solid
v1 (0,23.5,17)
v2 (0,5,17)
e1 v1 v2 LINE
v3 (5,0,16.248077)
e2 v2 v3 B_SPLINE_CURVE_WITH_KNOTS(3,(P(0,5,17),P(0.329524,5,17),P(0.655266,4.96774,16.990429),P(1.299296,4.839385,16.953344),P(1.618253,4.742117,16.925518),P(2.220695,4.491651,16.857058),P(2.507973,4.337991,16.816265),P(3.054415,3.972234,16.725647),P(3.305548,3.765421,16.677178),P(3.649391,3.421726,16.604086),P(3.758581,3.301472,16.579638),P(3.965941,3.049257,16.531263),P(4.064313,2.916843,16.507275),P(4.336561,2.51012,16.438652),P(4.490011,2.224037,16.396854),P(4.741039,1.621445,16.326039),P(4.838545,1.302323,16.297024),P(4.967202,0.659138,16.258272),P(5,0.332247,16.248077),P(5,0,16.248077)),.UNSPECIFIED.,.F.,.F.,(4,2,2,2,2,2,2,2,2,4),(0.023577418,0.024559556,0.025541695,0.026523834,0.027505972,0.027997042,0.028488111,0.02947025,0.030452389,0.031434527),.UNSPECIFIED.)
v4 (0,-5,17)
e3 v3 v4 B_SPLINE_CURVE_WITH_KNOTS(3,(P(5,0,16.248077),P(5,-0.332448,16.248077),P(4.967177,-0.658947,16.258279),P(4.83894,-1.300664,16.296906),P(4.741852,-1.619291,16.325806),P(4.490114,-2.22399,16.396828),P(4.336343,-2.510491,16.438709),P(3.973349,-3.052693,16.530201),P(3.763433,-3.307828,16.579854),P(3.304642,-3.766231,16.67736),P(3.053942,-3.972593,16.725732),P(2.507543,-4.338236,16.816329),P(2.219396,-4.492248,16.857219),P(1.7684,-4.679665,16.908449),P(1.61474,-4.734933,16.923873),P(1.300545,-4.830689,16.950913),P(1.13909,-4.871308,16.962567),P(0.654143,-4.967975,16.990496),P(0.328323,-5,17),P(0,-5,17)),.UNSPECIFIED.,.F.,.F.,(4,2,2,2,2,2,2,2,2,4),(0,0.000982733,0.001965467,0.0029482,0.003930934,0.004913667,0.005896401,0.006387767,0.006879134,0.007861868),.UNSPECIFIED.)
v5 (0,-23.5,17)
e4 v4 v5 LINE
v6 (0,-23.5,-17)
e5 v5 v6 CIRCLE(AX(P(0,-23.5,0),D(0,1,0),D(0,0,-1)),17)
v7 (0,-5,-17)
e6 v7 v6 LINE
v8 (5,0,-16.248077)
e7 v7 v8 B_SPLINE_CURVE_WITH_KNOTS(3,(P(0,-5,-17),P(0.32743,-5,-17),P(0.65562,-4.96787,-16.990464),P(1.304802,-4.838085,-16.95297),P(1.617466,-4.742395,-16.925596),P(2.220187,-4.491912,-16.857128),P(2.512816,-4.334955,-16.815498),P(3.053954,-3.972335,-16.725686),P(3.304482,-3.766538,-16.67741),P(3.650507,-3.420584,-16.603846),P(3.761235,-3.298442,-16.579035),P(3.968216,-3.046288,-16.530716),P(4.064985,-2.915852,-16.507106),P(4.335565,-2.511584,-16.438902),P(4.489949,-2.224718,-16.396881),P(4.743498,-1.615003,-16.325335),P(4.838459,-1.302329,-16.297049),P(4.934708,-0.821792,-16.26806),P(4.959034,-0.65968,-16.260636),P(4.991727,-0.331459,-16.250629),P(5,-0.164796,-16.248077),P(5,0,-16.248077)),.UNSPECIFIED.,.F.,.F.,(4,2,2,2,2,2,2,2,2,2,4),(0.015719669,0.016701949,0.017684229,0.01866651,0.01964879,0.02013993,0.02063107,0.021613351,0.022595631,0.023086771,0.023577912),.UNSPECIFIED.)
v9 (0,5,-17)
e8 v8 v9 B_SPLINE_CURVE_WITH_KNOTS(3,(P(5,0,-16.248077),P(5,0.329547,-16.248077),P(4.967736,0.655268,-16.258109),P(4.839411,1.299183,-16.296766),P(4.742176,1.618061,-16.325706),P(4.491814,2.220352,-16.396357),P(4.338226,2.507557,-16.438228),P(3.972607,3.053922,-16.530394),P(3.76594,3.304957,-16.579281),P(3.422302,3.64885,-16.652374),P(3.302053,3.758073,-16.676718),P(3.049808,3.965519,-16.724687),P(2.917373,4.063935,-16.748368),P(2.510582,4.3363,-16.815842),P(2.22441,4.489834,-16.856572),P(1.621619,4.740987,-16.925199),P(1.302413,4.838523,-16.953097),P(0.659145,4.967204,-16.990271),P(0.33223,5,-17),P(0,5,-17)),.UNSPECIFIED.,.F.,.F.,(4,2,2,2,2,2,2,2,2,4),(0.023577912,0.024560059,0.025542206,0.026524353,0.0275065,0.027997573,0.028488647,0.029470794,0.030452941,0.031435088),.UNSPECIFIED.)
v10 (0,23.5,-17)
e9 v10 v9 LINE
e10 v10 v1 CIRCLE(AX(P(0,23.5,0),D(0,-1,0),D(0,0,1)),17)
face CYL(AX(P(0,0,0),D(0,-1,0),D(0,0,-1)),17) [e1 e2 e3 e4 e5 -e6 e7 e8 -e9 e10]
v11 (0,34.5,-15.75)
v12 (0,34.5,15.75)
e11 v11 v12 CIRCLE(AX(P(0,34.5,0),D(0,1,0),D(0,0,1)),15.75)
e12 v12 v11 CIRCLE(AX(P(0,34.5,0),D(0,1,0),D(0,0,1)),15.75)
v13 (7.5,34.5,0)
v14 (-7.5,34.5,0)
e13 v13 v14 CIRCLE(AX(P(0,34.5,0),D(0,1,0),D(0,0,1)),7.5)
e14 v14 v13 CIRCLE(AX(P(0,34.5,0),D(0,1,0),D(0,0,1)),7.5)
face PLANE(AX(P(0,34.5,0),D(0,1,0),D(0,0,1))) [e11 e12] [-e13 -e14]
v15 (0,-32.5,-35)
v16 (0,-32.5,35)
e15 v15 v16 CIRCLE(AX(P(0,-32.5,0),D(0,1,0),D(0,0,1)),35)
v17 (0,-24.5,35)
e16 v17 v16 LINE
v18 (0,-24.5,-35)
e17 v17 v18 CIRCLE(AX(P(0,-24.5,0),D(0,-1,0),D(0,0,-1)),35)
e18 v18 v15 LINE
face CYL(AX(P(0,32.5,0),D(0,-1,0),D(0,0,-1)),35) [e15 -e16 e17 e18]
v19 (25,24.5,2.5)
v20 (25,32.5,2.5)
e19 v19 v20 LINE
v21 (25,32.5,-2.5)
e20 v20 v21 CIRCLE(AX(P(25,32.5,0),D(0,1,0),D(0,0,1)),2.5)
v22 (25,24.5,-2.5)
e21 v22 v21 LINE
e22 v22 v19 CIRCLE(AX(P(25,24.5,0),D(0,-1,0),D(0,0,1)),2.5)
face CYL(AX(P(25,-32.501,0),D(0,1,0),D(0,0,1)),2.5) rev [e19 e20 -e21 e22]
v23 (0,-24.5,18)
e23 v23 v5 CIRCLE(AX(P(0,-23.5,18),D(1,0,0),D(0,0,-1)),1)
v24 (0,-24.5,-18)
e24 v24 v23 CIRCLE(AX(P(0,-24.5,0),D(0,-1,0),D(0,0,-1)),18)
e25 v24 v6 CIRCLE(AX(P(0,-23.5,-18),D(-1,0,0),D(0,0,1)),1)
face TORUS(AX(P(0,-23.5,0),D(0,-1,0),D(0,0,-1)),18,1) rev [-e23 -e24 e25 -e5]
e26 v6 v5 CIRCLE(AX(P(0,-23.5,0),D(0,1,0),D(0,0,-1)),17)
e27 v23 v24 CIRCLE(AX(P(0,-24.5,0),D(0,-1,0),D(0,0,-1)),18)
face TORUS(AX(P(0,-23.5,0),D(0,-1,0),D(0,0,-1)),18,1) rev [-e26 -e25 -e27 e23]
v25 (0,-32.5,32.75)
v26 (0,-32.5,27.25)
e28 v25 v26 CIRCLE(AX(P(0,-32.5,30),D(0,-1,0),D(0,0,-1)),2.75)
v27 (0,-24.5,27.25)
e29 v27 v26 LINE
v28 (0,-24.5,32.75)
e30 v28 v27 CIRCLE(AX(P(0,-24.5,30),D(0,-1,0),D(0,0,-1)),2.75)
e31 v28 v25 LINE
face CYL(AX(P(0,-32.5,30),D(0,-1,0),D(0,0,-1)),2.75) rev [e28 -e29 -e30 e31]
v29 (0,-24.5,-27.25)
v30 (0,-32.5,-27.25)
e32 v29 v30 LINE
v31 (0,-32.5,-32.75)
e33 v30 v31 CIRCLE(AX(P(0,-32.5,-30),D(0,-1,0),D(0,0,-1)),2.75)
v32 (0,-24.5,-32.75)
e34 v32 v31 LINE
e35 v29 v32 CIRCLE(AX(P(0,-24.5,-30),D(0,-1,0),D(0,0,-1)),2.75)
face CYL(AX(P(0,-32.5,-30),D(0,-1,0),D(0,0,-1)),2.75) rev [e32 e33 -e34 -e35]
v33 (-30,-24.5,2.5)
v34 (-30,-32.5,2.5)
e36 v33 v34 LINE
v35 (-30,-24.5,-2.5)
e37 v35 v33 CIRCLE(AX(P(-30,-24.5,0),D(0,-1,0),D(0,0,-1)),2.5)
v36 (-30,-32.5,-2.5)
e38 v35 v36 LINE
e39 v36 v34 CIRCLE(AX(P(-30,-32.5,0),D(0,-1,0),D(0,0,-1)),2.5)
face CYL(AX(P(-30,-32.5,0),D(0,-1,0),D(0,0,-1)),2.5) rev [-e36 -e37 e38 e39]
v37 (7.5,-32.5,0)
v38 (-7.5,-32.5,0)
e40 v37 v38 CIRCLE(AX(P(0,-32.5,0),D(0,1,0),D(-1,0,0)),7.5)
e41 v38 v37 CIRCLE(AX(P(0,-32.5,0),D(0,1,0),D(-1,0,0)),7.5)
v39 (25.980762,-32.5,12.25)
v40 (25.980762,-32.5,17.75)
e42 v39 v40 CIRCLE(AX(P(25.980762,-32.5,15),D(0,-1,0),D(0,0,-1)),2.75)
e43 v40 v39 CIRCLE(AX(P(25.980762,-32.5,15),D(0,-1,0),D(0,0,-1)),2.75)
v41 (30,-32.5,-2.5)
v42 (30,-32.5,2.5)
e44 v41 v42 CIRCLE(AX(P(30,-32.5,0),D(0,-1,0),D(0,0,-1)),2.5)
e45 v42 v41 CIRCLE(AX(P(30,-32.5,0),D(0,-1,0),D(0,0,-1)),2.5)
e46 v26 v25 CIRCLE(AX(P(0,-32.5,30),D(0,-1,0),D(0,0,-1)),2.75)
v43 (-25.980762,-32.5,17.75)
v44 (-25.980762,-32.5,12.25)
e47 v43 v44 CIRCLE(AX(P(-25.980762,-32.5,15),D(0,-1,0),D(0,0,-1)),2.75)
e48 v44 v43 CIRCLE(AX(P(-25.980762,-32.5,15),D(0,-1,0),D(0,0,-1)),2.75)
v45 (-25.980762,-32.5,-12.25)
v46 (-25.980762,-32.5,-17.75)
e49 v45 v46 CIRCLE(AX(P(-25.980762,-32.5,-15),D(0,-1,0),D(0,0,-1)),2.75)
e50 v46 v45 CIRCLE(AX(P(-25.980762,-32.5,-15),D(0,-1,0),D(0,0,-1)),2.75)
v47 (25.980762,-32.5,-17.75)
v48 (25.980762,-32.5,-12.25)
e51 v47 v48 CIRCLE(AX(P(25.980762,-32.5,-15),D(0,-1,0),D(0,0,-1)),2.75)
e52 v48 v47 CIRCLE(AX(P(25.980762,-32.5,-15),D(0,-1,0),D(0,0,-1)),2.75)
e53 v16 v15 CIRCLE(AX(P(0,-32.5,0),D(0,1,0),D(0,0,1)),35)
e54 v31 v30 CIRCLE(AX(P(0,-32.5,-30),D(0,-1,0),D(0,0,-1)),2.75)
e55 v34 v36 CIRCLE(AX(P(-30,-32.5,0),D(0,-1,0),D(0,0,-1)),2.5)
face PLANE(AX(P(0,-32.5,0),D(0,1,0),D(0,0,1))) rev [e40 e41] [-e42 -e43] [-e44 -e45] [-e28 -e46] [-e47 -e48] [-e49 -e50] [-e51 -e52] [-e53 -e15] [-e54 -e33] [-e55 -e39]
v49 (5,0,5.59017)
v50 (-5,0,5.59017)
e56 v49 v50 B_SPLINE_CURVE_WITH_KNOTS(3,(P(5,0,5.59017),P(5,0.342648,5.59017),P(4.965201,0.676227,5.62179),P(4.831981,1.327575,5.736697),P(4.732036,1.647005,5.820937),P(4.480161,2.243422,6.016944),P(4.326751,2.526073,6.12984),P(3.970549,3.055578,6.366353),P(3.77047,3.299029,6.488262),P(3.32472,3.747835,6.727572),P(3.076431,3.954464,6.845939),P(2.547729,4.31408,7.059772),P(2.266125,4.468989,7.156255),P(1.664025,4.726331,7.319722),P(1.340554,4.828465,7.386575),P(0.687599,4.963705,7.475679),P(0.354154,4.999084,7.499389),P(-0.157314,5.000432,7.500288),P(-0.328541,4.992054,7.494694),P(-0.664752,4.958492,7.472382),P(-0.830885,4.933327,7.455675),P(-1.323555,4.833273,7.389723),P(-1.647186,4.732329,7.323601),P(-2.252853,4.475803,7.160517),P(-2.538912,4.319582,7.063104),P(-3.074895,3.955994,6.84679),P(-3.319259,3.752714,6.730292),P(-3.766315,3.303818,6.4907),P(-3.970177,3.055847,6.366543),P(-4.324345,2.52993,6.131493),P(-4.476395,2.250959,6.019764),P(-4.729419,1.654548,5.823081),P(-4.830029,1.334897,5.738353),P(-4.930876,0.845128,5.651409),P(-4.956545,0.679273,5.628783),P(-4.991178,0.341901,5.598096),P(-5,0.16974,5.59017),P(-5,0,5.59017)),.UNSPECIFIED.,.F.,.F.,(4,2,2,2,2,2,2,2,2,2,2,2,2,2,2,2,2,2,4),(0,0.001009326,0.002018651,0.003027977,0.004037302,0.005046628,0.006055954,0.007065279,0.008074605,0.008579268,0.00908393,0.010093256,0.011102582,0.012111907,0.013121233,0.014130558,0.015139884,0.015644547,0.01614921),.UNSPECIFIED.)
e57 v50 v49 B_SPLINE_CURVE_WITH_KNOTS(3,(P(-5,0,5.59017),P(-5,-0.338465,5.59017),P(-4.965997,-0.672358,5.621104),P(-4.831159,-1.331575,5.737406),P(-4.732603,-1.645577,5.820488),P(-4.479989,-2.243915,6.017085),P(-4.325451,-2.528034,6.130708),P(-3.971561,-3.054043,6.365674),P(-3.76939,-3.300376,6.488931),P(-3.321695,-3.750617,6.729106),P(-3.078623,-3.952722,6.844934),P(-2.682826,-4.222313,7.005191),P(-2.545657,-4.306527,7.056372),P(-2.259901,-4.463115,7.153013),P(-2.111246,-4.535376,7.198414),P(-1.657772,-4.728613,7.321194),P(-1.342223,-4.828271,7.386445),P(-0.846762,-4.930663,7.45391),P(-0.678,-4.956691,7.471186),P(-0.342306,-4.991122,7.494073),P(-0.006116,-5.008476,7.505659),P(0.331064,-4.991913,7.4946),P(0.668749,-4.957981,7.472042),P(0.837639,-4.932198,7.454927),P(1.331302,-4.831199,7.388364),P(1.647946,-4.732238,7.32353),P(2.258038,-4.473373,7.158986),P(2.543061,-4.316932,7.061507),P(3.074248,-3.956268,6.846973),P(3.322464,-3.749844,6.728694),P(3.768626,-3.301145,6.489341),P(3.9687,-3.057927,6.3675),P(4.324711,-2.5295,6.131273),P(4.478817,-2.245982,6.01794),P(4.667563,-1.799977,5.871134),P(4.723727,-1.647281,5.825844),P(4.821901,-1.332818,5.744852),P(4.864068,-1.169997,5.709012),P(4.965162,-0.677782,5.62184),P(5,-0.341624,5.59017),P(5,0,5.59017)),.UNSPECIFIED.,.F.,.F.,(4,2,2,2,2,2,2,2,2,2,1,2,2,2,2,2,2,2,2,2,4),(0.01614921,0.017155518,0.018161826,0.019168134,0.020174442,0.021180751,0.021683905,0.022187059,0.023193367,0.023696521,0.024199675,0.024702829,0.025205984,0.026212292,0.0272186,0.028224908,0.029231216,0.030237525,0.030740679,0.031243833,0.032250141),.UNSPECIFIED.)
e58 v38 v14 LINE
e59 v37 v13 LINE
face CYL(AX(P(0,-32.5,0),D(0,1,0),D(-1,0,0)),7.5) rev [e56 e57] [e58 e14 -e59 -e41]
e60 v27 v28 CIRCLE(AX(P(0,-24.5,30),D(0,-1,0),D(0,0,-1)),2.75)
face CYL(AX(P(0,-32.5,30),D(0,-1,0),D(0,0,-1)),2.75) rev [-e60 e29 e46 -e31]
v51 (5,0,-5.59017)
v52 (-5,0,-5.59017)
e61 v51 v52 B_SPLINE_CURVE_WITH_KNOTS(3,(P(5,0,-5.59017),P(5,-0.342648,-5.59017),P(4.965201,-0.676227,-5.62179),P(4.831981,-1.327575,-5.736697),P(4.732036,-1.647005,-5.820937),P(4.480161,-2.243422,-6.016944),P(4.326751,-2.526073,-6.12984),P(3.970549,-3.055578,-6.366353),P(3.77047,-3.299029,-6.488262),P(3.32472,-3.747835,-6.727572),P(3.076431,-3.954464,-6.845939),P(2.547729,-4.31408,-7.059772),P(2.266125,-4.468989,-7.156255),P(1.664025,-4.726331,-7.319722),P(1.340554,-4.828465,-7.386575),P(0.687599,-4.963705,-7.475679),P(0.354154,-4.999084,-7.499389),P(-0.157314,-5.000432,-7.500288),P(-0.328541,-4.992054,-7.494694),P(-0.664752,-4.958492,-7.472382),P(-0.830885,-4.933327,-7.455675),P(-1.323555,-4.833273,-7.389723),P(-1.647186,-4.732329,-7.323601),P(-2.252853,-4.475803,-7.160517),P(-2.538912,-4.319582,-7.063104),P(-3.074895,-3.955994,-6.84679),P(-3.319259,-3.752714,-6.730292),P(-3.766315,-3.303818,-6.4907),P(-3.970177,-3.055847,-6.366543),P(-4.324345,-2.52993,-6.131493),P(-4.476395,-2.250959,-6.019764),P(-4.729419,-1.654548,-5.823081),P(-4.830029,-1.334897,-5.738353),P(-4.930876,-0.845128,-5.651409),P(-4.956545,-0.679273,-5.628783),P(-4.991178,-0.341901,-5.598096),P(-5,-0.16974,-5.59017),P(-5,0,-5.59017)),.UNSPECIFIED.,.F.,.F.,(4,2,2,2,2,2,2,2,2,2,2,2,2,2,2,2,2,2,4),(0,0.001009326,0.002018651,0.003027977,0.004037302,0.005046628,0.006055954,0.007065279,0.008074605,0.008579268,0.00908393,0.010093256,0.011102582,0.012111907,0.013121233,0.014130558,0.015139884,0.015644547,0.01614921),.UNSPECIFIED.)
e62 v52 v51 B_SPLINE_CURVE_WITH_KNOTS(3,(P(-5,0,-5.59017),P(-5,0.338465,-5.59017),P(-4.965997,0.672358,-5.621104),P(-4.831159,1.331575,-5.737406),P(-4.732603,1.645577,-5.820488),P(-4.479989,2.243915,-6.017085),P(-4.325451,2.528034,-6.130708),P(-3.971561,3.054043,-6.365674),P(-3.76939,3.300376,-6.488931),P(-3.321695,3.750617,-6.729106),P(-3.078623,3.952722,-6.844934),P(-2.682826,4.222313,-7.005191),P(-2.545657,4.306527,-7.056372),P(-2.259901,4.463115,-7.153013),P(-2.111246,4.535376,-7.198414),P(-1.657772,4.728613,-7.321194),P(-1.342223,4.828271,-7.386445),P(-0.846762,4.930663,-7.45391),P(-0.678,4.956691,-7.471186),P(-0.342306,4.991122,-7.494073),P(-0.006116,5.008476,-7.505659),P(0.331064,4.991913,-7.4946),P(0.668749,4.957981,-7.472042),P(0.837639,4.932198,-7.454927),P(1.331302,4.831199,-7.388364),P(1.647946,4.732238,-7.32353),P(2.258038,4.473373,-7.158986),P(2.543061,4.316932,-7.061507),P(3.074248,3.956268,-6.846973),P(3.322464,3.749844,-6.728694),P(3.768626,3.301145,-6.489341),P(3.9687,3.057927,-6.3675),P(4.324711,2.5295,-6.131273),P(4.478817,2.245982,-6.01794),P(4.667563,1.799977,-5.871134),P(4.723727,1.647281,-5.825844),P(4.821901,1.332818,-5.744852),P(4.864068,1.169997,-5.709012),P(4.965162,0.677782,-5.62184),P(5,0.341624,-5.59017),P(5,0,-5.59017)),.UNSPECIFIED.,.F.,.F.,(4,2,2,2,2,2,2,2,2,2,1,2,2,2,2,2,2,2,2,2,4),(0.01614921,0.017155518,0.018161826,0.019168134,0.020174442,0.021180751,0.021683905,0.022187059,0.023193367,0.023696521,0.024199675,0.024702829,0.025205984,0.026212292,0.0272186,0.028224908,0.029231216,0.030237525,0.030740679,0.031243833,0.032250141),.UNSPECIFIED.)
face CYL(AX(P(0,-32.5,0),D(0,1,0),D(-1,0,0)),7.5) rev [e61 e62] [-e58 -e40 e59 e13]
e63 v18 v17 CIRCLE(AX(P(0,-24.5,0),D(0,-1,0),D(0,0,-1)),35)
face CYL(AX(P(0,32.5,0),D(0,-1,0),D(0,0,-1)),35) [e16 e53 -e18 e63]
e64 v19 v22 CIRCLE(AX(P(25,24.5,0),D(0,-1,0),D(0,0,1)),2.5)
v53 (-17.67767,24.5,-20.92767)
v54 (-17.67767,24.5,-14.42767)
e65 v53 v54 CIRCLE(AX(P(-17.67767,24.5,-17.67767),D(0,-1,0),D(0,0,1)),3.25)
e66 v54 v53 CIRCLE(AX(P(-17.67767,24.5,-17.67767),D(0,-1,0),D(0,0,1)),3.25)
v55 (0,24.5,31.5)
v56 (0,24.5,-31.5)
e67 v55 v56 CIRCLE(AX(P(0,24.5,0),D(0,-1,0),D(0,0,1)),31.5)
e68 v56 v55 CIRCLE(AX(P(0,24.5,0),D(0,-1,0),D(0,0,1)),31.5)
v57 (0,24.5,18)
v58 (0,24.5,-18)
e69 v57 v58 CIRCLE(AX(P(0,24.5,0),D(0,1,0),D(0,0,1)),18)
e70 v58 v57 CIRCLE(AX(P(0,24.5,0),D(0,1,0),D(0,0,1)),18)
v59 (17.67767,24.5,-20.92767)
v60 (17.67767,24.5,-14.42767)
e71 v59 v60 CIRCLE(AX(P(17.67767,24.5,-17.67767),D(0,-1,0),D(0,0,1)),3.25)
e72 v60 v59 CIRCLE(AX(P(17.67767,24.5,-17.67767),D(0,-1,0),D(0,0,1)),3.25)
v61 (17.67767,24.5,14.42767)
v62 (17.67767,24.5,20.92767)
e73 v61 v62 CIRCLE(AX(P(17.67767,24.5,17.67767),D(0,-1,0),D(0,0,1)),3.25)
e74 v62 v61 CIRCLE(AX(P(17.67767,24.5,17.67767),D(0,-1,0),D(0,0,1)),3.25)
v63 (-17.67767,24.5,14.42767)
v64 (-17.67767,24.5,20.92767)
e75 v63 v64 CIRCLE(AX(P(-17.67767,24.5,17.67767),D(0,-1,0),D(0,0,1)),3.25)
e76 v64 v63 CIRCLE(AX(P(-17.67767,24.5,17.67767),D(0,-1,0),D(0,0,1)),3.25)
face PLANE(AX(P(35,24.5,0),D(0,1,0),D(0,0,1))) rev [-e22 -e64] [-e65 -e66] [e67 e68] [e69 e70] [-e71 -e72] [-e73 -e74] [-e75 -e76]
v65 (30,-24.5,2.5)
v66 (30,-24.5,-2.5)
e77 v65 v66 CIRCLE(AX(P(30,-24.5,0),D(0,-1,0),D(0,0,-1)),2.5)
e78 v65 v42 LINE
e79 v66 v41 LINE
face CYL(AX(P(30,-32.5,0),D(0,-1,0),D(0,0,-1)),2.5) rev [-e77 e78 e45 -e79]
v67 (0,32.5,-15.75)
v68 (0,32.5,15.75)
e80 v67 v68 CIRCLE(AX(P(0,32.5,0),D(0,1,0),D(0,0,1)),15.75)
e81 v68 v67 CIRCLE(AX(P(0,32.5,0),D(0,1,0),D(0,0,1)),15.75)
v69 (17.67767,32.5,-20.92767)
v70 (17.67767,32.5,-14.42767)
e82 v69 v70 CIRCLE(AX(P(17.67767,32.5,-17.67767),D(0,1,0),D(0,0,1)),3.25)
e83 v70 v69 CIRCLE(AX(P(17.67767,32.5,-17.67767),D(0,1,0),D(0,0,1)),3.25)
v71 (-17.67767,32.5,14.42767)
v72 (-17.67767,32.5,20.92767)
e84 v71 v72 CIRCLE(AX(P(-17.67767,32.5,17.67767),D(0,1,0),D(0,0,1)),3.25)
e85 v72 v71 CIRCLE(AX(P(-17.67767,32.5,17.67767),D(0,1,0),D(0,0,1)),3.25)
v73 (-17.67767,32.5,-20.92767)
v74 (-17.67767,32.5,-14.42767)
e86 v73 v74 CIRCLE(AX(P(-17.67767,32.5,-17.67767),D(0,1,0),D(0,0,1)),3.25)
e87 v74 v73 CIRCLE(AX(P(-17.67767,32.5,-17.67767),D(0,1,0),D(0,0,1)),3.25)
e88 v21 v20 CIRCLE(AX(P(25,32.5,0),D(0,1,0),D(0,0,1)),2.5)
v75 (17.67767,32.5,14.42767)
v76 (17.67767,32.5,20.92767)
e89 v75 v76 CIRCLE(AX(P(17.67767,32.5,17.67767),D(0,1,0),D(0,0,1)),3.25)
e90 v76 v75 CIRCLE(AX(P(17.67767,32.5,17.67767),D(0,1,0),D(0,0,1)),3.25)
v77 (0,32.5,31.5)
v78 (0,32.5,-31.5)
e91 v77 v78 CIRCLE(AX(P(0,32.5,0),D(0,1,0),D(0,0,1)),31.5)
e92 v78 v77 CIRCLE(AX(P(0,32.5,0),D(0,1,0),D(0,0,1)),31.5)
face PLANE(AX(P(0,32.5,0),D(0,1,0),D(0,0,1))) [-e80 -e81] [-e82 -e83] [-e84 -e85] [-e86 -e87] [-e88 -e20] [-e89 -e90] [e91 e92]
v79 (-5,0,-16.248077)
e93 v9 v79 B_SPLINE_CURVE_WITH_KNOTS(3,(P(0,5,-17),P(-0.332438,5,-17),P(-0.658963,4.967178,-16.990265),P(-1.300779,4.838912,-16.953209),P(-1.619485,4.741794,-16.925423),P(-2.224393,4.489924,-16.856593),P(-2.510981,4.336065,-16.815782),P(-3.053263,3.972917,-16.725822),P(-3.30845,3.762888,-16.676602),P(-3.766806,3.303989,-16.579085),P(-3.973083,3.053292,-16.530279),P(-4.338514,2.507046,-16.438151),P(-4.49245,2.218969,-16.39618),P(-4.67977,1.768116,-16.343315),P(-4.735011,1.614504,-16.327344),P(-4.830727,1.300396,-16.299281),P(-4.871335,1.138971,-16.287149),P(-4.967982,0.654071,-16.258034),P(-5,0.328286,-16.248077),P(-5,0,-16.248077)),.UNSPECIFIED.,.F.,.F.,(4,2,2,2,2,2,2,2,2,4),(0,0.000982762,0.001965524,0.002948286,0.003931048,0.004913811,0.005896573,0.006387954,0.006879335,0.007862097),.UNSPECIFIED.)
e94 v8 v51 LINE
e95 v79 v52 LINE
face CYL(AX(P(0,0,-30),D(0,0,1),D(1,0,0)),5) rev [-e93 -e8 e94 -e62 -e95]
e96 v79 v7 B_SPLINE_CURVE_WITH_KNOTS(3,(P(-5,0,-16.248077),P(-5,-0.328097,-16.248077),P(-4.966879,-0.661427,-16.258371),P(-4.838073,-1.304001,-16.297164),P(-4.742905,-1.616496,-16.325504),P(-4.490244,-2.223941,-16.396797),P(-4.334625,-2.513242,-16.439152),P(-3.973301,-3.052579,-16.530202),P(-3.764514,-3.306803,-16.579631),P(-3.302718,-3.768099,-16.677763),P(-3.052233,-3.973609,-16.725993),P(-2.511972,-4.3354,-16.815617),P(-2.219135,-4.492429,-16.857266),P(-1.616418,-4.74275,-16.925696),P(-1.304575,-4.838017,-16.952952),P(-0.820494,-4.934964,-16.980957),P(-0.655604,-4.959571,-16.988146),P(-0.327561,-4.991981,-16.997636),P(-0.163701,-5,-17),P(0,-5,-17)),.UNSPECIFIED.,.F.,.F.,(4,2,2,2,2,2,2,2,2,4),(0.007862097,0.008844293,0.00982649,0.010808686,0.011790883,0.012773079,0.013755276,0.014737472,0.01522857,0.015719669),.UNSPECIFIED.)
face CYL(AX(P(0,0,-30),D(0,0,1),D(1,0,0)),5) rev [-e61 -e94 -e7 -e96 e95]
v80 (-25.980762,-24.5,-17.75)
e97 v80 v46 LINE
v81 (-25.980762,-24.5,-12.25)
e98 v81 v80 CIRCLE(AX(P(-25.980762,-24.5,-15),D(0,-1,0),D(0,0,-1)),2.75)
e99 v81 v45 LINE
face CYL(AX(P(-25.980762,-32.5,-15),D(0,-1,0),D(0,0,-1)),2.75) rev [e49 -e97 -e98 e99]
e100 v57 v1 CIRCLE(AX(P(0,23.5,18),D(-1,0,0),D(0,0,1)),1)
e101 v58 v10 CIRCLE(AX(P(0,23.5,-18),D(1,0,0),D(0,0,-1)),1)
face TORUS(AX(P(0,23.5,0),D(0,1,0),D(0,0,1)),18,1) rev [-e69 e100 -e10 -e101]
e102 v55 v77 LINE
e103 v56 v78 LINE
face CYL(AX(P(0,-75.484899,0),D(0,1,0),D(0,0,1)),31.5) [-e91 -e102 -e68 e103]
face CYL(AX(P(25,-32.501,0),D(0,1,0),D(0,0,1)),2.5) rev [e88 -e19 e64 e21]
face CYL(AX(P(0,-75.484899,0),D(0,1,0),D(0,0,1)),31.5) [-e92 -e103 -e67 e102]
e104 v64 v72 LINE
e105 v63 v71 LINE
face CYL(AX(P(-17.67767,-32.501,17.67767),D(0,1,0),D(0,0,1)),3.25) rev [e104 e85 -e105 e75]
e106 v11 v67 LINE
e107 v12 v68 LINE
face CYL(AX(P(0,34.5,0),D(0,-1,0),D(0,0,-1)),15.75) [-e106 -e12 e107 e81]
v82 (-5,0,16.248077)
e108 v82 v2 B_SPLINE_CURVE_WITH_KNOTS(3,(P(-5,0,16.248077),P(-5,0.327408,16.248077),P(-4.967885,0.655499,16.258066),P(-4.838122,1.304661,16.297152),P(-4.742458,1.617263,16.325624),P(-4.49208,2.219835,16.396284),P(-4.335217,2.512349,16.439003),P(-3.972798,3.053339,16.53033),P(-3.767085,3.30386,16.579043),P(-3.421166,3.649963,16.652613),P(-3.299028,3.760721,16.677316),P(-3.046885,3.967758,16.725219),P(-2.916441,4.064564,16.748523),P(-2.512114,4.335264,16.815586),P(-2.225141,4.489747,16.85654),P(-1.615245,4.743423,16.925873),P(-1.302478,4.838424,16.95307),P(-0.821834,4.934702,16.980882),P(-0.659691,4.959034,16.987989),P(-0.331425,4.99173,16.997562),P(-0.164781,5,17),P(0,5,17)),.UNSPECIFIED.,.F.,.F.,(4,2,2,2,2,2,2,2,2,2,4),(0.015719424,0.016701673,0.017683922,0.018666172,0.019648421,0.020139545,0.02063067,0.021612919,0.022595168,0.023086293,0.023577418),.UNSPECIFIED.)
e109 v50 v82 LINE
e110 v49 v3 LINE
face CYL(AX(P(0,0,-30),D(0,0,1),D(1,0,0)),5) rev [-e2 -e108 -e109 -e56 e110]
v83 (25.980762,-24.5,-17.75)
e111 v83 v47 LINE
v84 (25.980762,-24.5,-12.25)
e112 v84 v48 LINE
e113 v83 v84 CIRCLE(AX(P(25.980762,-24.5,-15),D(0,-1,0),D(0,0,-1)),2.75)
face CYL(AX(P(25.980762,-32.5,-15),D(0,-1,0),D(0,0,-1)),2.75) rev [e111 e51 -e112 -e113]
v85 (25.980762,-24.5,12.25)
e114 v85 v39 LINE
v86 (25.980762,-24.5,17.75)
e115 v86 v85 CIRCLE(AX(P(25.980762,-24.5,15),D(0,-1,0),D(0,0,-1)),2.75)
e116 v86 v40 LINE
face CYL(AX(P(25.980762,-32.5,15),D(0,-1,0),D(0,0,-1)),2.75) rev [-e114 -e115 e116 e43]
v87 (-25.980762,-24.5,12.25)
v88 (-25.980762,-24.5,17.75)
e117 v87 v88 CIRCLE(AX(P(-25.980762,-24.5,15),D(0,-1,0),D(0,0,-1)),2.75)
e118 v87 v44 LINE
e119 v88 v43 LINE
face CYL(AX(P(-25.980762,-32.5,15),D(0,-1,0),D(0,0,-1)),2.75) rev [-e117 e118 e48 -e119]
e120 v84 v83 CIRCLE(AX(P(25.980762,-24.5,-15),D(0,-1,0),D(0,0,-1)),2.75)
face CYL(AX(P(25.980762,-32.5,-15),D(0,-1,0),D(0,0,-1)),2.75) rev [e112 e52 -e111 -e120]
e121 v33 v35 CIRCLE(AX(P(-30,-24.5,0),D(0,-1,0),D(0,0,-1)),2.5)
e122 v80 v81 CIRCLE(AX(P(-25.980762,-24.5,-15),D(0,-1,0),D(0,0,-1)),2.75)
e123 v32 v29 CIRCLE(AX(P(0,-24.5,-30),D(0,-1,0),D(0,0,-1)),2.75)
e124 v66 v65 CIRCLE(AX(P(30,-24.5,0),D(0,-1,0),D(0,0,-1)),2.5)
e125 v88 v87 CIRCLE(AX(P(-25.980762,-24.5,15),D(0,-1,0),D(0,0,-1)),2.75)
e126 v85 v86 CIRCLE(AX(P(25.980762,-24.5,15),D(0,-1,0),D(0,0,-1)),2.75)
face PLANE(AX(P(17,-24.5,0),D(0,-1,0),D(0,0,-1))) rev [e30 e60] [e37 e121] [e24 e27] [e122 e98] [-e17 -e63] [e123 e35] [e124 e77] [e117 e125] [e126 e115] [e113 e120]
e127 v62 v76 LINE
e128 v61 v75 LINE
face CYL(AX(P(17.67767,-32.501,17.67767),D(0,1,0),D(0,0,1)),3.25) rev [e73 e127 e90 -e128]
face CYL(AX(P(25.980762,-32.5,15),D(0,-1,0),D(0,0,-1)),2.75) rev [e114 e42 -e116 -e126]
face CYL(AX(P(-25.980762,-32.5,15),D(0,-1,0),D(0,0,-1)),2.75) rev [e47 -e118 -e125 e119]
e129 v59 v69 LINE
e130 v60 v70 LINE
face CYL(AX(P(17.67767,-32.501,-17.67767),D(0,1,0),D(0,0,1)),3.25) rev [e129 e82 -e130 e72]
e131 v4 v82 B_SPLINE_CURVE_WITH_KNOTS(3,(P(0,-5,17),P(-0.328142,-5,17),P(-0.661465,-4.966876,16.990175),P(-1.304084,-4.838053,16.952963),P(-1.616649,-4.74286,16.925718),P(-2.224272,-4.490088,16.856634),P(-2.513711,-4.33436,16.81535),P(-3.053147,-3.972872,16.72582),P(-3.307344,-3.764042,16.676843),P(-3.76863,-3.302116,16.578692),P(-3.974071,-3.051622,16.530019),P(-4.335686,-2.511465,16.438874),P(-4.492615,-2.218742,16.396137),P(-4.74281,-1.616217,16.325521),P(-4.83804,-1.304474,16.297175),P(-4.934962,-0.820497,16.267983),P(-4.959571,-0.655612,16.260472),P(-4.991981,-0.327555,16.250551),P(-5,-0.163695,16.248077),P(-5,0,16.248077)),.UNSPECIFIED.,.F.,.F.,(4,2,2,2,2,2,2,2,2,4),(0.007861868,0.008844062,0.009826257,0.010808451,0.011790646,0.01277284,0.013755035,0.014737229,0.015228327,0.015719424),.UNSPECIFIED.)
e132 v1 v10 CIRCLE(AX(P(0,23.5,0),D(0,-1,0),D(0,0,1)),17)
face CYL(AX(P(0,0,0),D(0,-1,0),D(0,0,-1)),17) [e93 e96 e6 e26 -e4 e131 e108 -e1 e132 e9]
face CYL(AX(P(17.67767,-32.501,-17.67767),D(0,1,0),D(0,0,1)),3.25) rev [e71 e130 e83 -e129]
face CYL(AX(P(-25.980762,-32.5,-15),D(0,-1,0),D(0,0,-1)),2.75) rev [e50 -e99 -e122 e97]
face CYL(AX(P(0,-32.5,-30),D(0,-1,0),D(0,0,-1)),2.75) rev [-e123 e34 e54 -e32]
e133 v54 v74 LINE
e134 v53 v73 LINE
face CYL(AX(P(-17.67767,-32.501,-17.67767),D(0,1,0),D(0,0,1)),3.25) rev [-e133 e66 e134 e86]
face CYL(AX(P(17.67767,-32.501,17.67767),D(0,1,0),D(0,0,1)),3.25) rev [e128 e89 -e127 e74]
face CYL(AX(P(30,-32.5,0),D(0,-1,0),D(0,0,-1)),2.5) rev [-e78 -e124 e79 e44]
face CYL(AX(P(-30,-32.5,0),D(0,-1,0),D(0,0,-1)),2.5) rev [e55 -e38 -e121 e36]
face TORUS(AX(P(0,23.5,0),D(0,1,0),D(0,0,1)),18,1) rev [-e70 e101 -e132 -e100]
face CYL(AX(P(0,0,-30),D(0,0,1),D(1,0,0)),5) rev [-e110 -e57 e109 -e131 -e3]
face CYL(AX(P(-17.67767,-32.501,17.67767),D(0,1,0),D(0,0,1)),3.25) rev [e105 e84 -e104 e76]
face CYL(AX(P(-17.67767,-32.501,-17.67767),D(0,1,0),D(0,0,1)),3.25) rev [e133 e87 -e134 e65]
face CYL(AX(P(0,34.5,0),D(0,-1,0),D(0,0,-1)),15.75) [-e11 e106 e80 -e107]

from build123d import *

# Parameters (mm, degrees)
SKETCH_1_R             = 35
EXTRUDE_1_DEPTH        = 32.5
SKETCH_3_W             = 18
SKETCH_3_H             = 49
FILLET_1_R             = 1
SKETCH_6_R             = 7.5
CUT_EXTRUDE_3_DEPTH    = 82.700673192
HOLE_WIZARD_M5_1_D     = 5.5
HOLE_WIZARD_M5_1_DEPTH = 15
HOLE_WIZARD_M5_1_TIP   = 1.652366702
F_5_0MM_1_D            = 5
F_5_0MM_1_DEPTH        = 10
F_5_0MM_1_TIP          = 1.502151548
SKETCH_11_R            = 5
CUT_EXTRUDE_4_DEPTH    = 30
SKETCH_15_OUTSIDE_W    = 95.686
SKETCH_15_OUTSIDE_H    = 95.686
SKETCH_15_OUTSIDE_R    = 31.5
CUT_EXTRUDE_6_DEPTH    = 8
EXTRUDE_START          = 2
SKETCH_16_R            = 15.75
SKETCH_16_R_2          = 7.5
EXTRUDE_2_DEPTH        = 2
SKETCH_17_R            = 3.25
SKETCH_17_R_2          = 2.5
CUT_EXTRUDE_7_DEPTH    = 8


with BuildPart() as part:
    # 草图1 → 凸台-拉伸1 (new, symmetric)
    with BuildSketch(Plane(origin=(0, 0, 0), x_dir=(1, 0, 0), z_dir=(0, 1, 0))):
        with Locations(Location((0, 0, 0), (0, 0, 270))):
            Circle(SKETCH_1_R)
    extrude(amount=EXTRUDE_1_DEPTH, both=True)

    # 草图3 → 切除-旋转1 (revolve, cut)
    with BuildSketch(Plane.XY, mode=Mode.PRIVATE) as cut_revolve_1_sk:
        with Locations((26, 0)):
            Rectangle(SKETCH_3_W, SKETCH_3_H)
    revolve(cut_revolve_1_sk.sketch.rotate(Axis((0, 0, 0), (0, 1, 0)), 90), axis=Axis((0, 0, 0), (0, 1, 0)), mode=Mode.SUBTRACT)

    # 圆角1
    fillet_1_edges = [part.edges().sort_by_distance(p)[0] for p in [
        (0, 24.5, 17),
        (0, -24.5, 17),
    ]]
    fillet(fillet_1_edges, radius=FILLET_1_R)

    # 草图6 → 切除-拉伸3 (cut, through all)
    with BuildSketch(Plane(origin=(0, 32.5, 0), x_dir=(1, 0, 0), z_dir=(0, 1, 0))):
        with Locations(Location((0, 0, 0), (0, 0, 180))):
            Circle(SKETCH_6_R)
    extrude(amount=-CUT_EXTRUDE_3_DEPTH, mode=Mode.SUBTRACT)

    # M5 间隙孔1
    with Locations(Plane(origin=(0, -32.5, 0), x_dir=(-1, 0, 0), z_dir=(0, -1, 0))):
        with Locations((0, -30), (-25.980762114, -15), (-25.980762114, 15), (0, 30), (25.980762114, 15), (25.980762114, -15)):
            Hole(HOLE_WIZARD_M5_1_D / 2, depth=HOLE_WIZARD_M5_1_DEPTH)
            with Locations((0, 0, -(HOLE_WIZARD_M5_1_DEPTH + HOLE_WIZARD_M5_1_TIP / 2))):  # 118° drill point
                Cone(0, HOLE_WIZARD_M5_1_D / 2, HOLE_WIZARD_M5_1_TIP, mode=Mode.SUBTRACT)

    # Ø5.0mm 暗销孔1
    with Locations(Plane(origin=(0, -32.5, 0), x_dir=(-1, 0, 0), z_dir=(0, -1, 0))):
        with Locations((-30, 0), (30, 0)):
            Hole(F_5_0MM_1_D / 2, depth=F_5_0MM_1_DEPTH)
            with Locations((0, 0, -(F_5_0MM_1_DEPTH + F_5_0MM_1_TIP / 2))):  # 118° drill point
                Cone(0, F_5_0MM_1_D / 2, F_5_0MM_1_TIP, mode=Mode.SUBTRACT)

    # 草图11 → 切除-拉伸4 (cut, symmetric)
    with BuildSketch(Plane.XY):
        Circle(SKETCH_11_R)
    extrude(amount=CUT_EXTRUDE_4_DEPTH, both=True, mode=Mode.SUBTRACT)

    # 草图15 outside → 切除-拉伸6 (cut)
    with BuildSketch(Plane(origin=(0, 32.5, 0), x_dir=(1, 0, 0), z_dir=(0, 1, 0))):
        Rectangle(SKETCH_15_OUTSIDE_W, SKETCH_15_OUTSIDE_H)
        with Locations(Location((0, 0, 0), (0, 0, 270))):
            Circle(SKETCH_15_OUTSIDE_R, mode=Mode.SUBTRACT)
    extrude(amount=-CUT_EXTRUDE_6_DEPTH, mode=Mode.SUBTRACT)

    # 草图16 → 凸台-拉伸2 (add)
    with BuildSketch(Plane(origin=(0, 32.5, 0), x_dir=(1, 0, 0), z_dir=(0, 1, 0)).offset(EXTRUDE_START)):
        with Locations(Location((0, 0, 0), (0, 0, 270))):
            Circle(SKETCH_16_R)
        with Locations(Location((0, 0, 0), (0, 0, 180))):
            Circle(SKETCH_16_R_2, mode=Mode.SUBTRACT)
    extrude(amount=-EXTRUDE_2_DEPTH)

    # 草图17 → 切除-拉伸7 (cut)
    with BuildSketch(Plane(origin=(0, 32.5, 0), x_dir=(1, 0, 0), z_dir=(0, 1, 0))):
        with Locations(Location((-17.67766953, -17.67766953, 0), (0, 0, 270))):
            Circle(SKETCH_17_R)
        with Locations(Location((-17.67766953, 17.67766953, 0), (0, 0, 270))):
            Circle(SKETCH_17_R)
        with Locations(Location((17.67766953, 17.67766953, 0), (0, 0, 270))):
            Circle(SKETCH_17_R)
        with Locations(Location((17.67766953, -17.67766953, 0), (0, 0, 270))):
            Circle(SKETCH_17_R)
        with Locations(Location((25, 0, 0), (0, 0, 270))):
            Circle(SKETCH_17_R_2)
    extrude(amount=-CUT_EXTRUDE_7_DEPTH, mode=Mode.SUBTRACT)


solid = part.part
